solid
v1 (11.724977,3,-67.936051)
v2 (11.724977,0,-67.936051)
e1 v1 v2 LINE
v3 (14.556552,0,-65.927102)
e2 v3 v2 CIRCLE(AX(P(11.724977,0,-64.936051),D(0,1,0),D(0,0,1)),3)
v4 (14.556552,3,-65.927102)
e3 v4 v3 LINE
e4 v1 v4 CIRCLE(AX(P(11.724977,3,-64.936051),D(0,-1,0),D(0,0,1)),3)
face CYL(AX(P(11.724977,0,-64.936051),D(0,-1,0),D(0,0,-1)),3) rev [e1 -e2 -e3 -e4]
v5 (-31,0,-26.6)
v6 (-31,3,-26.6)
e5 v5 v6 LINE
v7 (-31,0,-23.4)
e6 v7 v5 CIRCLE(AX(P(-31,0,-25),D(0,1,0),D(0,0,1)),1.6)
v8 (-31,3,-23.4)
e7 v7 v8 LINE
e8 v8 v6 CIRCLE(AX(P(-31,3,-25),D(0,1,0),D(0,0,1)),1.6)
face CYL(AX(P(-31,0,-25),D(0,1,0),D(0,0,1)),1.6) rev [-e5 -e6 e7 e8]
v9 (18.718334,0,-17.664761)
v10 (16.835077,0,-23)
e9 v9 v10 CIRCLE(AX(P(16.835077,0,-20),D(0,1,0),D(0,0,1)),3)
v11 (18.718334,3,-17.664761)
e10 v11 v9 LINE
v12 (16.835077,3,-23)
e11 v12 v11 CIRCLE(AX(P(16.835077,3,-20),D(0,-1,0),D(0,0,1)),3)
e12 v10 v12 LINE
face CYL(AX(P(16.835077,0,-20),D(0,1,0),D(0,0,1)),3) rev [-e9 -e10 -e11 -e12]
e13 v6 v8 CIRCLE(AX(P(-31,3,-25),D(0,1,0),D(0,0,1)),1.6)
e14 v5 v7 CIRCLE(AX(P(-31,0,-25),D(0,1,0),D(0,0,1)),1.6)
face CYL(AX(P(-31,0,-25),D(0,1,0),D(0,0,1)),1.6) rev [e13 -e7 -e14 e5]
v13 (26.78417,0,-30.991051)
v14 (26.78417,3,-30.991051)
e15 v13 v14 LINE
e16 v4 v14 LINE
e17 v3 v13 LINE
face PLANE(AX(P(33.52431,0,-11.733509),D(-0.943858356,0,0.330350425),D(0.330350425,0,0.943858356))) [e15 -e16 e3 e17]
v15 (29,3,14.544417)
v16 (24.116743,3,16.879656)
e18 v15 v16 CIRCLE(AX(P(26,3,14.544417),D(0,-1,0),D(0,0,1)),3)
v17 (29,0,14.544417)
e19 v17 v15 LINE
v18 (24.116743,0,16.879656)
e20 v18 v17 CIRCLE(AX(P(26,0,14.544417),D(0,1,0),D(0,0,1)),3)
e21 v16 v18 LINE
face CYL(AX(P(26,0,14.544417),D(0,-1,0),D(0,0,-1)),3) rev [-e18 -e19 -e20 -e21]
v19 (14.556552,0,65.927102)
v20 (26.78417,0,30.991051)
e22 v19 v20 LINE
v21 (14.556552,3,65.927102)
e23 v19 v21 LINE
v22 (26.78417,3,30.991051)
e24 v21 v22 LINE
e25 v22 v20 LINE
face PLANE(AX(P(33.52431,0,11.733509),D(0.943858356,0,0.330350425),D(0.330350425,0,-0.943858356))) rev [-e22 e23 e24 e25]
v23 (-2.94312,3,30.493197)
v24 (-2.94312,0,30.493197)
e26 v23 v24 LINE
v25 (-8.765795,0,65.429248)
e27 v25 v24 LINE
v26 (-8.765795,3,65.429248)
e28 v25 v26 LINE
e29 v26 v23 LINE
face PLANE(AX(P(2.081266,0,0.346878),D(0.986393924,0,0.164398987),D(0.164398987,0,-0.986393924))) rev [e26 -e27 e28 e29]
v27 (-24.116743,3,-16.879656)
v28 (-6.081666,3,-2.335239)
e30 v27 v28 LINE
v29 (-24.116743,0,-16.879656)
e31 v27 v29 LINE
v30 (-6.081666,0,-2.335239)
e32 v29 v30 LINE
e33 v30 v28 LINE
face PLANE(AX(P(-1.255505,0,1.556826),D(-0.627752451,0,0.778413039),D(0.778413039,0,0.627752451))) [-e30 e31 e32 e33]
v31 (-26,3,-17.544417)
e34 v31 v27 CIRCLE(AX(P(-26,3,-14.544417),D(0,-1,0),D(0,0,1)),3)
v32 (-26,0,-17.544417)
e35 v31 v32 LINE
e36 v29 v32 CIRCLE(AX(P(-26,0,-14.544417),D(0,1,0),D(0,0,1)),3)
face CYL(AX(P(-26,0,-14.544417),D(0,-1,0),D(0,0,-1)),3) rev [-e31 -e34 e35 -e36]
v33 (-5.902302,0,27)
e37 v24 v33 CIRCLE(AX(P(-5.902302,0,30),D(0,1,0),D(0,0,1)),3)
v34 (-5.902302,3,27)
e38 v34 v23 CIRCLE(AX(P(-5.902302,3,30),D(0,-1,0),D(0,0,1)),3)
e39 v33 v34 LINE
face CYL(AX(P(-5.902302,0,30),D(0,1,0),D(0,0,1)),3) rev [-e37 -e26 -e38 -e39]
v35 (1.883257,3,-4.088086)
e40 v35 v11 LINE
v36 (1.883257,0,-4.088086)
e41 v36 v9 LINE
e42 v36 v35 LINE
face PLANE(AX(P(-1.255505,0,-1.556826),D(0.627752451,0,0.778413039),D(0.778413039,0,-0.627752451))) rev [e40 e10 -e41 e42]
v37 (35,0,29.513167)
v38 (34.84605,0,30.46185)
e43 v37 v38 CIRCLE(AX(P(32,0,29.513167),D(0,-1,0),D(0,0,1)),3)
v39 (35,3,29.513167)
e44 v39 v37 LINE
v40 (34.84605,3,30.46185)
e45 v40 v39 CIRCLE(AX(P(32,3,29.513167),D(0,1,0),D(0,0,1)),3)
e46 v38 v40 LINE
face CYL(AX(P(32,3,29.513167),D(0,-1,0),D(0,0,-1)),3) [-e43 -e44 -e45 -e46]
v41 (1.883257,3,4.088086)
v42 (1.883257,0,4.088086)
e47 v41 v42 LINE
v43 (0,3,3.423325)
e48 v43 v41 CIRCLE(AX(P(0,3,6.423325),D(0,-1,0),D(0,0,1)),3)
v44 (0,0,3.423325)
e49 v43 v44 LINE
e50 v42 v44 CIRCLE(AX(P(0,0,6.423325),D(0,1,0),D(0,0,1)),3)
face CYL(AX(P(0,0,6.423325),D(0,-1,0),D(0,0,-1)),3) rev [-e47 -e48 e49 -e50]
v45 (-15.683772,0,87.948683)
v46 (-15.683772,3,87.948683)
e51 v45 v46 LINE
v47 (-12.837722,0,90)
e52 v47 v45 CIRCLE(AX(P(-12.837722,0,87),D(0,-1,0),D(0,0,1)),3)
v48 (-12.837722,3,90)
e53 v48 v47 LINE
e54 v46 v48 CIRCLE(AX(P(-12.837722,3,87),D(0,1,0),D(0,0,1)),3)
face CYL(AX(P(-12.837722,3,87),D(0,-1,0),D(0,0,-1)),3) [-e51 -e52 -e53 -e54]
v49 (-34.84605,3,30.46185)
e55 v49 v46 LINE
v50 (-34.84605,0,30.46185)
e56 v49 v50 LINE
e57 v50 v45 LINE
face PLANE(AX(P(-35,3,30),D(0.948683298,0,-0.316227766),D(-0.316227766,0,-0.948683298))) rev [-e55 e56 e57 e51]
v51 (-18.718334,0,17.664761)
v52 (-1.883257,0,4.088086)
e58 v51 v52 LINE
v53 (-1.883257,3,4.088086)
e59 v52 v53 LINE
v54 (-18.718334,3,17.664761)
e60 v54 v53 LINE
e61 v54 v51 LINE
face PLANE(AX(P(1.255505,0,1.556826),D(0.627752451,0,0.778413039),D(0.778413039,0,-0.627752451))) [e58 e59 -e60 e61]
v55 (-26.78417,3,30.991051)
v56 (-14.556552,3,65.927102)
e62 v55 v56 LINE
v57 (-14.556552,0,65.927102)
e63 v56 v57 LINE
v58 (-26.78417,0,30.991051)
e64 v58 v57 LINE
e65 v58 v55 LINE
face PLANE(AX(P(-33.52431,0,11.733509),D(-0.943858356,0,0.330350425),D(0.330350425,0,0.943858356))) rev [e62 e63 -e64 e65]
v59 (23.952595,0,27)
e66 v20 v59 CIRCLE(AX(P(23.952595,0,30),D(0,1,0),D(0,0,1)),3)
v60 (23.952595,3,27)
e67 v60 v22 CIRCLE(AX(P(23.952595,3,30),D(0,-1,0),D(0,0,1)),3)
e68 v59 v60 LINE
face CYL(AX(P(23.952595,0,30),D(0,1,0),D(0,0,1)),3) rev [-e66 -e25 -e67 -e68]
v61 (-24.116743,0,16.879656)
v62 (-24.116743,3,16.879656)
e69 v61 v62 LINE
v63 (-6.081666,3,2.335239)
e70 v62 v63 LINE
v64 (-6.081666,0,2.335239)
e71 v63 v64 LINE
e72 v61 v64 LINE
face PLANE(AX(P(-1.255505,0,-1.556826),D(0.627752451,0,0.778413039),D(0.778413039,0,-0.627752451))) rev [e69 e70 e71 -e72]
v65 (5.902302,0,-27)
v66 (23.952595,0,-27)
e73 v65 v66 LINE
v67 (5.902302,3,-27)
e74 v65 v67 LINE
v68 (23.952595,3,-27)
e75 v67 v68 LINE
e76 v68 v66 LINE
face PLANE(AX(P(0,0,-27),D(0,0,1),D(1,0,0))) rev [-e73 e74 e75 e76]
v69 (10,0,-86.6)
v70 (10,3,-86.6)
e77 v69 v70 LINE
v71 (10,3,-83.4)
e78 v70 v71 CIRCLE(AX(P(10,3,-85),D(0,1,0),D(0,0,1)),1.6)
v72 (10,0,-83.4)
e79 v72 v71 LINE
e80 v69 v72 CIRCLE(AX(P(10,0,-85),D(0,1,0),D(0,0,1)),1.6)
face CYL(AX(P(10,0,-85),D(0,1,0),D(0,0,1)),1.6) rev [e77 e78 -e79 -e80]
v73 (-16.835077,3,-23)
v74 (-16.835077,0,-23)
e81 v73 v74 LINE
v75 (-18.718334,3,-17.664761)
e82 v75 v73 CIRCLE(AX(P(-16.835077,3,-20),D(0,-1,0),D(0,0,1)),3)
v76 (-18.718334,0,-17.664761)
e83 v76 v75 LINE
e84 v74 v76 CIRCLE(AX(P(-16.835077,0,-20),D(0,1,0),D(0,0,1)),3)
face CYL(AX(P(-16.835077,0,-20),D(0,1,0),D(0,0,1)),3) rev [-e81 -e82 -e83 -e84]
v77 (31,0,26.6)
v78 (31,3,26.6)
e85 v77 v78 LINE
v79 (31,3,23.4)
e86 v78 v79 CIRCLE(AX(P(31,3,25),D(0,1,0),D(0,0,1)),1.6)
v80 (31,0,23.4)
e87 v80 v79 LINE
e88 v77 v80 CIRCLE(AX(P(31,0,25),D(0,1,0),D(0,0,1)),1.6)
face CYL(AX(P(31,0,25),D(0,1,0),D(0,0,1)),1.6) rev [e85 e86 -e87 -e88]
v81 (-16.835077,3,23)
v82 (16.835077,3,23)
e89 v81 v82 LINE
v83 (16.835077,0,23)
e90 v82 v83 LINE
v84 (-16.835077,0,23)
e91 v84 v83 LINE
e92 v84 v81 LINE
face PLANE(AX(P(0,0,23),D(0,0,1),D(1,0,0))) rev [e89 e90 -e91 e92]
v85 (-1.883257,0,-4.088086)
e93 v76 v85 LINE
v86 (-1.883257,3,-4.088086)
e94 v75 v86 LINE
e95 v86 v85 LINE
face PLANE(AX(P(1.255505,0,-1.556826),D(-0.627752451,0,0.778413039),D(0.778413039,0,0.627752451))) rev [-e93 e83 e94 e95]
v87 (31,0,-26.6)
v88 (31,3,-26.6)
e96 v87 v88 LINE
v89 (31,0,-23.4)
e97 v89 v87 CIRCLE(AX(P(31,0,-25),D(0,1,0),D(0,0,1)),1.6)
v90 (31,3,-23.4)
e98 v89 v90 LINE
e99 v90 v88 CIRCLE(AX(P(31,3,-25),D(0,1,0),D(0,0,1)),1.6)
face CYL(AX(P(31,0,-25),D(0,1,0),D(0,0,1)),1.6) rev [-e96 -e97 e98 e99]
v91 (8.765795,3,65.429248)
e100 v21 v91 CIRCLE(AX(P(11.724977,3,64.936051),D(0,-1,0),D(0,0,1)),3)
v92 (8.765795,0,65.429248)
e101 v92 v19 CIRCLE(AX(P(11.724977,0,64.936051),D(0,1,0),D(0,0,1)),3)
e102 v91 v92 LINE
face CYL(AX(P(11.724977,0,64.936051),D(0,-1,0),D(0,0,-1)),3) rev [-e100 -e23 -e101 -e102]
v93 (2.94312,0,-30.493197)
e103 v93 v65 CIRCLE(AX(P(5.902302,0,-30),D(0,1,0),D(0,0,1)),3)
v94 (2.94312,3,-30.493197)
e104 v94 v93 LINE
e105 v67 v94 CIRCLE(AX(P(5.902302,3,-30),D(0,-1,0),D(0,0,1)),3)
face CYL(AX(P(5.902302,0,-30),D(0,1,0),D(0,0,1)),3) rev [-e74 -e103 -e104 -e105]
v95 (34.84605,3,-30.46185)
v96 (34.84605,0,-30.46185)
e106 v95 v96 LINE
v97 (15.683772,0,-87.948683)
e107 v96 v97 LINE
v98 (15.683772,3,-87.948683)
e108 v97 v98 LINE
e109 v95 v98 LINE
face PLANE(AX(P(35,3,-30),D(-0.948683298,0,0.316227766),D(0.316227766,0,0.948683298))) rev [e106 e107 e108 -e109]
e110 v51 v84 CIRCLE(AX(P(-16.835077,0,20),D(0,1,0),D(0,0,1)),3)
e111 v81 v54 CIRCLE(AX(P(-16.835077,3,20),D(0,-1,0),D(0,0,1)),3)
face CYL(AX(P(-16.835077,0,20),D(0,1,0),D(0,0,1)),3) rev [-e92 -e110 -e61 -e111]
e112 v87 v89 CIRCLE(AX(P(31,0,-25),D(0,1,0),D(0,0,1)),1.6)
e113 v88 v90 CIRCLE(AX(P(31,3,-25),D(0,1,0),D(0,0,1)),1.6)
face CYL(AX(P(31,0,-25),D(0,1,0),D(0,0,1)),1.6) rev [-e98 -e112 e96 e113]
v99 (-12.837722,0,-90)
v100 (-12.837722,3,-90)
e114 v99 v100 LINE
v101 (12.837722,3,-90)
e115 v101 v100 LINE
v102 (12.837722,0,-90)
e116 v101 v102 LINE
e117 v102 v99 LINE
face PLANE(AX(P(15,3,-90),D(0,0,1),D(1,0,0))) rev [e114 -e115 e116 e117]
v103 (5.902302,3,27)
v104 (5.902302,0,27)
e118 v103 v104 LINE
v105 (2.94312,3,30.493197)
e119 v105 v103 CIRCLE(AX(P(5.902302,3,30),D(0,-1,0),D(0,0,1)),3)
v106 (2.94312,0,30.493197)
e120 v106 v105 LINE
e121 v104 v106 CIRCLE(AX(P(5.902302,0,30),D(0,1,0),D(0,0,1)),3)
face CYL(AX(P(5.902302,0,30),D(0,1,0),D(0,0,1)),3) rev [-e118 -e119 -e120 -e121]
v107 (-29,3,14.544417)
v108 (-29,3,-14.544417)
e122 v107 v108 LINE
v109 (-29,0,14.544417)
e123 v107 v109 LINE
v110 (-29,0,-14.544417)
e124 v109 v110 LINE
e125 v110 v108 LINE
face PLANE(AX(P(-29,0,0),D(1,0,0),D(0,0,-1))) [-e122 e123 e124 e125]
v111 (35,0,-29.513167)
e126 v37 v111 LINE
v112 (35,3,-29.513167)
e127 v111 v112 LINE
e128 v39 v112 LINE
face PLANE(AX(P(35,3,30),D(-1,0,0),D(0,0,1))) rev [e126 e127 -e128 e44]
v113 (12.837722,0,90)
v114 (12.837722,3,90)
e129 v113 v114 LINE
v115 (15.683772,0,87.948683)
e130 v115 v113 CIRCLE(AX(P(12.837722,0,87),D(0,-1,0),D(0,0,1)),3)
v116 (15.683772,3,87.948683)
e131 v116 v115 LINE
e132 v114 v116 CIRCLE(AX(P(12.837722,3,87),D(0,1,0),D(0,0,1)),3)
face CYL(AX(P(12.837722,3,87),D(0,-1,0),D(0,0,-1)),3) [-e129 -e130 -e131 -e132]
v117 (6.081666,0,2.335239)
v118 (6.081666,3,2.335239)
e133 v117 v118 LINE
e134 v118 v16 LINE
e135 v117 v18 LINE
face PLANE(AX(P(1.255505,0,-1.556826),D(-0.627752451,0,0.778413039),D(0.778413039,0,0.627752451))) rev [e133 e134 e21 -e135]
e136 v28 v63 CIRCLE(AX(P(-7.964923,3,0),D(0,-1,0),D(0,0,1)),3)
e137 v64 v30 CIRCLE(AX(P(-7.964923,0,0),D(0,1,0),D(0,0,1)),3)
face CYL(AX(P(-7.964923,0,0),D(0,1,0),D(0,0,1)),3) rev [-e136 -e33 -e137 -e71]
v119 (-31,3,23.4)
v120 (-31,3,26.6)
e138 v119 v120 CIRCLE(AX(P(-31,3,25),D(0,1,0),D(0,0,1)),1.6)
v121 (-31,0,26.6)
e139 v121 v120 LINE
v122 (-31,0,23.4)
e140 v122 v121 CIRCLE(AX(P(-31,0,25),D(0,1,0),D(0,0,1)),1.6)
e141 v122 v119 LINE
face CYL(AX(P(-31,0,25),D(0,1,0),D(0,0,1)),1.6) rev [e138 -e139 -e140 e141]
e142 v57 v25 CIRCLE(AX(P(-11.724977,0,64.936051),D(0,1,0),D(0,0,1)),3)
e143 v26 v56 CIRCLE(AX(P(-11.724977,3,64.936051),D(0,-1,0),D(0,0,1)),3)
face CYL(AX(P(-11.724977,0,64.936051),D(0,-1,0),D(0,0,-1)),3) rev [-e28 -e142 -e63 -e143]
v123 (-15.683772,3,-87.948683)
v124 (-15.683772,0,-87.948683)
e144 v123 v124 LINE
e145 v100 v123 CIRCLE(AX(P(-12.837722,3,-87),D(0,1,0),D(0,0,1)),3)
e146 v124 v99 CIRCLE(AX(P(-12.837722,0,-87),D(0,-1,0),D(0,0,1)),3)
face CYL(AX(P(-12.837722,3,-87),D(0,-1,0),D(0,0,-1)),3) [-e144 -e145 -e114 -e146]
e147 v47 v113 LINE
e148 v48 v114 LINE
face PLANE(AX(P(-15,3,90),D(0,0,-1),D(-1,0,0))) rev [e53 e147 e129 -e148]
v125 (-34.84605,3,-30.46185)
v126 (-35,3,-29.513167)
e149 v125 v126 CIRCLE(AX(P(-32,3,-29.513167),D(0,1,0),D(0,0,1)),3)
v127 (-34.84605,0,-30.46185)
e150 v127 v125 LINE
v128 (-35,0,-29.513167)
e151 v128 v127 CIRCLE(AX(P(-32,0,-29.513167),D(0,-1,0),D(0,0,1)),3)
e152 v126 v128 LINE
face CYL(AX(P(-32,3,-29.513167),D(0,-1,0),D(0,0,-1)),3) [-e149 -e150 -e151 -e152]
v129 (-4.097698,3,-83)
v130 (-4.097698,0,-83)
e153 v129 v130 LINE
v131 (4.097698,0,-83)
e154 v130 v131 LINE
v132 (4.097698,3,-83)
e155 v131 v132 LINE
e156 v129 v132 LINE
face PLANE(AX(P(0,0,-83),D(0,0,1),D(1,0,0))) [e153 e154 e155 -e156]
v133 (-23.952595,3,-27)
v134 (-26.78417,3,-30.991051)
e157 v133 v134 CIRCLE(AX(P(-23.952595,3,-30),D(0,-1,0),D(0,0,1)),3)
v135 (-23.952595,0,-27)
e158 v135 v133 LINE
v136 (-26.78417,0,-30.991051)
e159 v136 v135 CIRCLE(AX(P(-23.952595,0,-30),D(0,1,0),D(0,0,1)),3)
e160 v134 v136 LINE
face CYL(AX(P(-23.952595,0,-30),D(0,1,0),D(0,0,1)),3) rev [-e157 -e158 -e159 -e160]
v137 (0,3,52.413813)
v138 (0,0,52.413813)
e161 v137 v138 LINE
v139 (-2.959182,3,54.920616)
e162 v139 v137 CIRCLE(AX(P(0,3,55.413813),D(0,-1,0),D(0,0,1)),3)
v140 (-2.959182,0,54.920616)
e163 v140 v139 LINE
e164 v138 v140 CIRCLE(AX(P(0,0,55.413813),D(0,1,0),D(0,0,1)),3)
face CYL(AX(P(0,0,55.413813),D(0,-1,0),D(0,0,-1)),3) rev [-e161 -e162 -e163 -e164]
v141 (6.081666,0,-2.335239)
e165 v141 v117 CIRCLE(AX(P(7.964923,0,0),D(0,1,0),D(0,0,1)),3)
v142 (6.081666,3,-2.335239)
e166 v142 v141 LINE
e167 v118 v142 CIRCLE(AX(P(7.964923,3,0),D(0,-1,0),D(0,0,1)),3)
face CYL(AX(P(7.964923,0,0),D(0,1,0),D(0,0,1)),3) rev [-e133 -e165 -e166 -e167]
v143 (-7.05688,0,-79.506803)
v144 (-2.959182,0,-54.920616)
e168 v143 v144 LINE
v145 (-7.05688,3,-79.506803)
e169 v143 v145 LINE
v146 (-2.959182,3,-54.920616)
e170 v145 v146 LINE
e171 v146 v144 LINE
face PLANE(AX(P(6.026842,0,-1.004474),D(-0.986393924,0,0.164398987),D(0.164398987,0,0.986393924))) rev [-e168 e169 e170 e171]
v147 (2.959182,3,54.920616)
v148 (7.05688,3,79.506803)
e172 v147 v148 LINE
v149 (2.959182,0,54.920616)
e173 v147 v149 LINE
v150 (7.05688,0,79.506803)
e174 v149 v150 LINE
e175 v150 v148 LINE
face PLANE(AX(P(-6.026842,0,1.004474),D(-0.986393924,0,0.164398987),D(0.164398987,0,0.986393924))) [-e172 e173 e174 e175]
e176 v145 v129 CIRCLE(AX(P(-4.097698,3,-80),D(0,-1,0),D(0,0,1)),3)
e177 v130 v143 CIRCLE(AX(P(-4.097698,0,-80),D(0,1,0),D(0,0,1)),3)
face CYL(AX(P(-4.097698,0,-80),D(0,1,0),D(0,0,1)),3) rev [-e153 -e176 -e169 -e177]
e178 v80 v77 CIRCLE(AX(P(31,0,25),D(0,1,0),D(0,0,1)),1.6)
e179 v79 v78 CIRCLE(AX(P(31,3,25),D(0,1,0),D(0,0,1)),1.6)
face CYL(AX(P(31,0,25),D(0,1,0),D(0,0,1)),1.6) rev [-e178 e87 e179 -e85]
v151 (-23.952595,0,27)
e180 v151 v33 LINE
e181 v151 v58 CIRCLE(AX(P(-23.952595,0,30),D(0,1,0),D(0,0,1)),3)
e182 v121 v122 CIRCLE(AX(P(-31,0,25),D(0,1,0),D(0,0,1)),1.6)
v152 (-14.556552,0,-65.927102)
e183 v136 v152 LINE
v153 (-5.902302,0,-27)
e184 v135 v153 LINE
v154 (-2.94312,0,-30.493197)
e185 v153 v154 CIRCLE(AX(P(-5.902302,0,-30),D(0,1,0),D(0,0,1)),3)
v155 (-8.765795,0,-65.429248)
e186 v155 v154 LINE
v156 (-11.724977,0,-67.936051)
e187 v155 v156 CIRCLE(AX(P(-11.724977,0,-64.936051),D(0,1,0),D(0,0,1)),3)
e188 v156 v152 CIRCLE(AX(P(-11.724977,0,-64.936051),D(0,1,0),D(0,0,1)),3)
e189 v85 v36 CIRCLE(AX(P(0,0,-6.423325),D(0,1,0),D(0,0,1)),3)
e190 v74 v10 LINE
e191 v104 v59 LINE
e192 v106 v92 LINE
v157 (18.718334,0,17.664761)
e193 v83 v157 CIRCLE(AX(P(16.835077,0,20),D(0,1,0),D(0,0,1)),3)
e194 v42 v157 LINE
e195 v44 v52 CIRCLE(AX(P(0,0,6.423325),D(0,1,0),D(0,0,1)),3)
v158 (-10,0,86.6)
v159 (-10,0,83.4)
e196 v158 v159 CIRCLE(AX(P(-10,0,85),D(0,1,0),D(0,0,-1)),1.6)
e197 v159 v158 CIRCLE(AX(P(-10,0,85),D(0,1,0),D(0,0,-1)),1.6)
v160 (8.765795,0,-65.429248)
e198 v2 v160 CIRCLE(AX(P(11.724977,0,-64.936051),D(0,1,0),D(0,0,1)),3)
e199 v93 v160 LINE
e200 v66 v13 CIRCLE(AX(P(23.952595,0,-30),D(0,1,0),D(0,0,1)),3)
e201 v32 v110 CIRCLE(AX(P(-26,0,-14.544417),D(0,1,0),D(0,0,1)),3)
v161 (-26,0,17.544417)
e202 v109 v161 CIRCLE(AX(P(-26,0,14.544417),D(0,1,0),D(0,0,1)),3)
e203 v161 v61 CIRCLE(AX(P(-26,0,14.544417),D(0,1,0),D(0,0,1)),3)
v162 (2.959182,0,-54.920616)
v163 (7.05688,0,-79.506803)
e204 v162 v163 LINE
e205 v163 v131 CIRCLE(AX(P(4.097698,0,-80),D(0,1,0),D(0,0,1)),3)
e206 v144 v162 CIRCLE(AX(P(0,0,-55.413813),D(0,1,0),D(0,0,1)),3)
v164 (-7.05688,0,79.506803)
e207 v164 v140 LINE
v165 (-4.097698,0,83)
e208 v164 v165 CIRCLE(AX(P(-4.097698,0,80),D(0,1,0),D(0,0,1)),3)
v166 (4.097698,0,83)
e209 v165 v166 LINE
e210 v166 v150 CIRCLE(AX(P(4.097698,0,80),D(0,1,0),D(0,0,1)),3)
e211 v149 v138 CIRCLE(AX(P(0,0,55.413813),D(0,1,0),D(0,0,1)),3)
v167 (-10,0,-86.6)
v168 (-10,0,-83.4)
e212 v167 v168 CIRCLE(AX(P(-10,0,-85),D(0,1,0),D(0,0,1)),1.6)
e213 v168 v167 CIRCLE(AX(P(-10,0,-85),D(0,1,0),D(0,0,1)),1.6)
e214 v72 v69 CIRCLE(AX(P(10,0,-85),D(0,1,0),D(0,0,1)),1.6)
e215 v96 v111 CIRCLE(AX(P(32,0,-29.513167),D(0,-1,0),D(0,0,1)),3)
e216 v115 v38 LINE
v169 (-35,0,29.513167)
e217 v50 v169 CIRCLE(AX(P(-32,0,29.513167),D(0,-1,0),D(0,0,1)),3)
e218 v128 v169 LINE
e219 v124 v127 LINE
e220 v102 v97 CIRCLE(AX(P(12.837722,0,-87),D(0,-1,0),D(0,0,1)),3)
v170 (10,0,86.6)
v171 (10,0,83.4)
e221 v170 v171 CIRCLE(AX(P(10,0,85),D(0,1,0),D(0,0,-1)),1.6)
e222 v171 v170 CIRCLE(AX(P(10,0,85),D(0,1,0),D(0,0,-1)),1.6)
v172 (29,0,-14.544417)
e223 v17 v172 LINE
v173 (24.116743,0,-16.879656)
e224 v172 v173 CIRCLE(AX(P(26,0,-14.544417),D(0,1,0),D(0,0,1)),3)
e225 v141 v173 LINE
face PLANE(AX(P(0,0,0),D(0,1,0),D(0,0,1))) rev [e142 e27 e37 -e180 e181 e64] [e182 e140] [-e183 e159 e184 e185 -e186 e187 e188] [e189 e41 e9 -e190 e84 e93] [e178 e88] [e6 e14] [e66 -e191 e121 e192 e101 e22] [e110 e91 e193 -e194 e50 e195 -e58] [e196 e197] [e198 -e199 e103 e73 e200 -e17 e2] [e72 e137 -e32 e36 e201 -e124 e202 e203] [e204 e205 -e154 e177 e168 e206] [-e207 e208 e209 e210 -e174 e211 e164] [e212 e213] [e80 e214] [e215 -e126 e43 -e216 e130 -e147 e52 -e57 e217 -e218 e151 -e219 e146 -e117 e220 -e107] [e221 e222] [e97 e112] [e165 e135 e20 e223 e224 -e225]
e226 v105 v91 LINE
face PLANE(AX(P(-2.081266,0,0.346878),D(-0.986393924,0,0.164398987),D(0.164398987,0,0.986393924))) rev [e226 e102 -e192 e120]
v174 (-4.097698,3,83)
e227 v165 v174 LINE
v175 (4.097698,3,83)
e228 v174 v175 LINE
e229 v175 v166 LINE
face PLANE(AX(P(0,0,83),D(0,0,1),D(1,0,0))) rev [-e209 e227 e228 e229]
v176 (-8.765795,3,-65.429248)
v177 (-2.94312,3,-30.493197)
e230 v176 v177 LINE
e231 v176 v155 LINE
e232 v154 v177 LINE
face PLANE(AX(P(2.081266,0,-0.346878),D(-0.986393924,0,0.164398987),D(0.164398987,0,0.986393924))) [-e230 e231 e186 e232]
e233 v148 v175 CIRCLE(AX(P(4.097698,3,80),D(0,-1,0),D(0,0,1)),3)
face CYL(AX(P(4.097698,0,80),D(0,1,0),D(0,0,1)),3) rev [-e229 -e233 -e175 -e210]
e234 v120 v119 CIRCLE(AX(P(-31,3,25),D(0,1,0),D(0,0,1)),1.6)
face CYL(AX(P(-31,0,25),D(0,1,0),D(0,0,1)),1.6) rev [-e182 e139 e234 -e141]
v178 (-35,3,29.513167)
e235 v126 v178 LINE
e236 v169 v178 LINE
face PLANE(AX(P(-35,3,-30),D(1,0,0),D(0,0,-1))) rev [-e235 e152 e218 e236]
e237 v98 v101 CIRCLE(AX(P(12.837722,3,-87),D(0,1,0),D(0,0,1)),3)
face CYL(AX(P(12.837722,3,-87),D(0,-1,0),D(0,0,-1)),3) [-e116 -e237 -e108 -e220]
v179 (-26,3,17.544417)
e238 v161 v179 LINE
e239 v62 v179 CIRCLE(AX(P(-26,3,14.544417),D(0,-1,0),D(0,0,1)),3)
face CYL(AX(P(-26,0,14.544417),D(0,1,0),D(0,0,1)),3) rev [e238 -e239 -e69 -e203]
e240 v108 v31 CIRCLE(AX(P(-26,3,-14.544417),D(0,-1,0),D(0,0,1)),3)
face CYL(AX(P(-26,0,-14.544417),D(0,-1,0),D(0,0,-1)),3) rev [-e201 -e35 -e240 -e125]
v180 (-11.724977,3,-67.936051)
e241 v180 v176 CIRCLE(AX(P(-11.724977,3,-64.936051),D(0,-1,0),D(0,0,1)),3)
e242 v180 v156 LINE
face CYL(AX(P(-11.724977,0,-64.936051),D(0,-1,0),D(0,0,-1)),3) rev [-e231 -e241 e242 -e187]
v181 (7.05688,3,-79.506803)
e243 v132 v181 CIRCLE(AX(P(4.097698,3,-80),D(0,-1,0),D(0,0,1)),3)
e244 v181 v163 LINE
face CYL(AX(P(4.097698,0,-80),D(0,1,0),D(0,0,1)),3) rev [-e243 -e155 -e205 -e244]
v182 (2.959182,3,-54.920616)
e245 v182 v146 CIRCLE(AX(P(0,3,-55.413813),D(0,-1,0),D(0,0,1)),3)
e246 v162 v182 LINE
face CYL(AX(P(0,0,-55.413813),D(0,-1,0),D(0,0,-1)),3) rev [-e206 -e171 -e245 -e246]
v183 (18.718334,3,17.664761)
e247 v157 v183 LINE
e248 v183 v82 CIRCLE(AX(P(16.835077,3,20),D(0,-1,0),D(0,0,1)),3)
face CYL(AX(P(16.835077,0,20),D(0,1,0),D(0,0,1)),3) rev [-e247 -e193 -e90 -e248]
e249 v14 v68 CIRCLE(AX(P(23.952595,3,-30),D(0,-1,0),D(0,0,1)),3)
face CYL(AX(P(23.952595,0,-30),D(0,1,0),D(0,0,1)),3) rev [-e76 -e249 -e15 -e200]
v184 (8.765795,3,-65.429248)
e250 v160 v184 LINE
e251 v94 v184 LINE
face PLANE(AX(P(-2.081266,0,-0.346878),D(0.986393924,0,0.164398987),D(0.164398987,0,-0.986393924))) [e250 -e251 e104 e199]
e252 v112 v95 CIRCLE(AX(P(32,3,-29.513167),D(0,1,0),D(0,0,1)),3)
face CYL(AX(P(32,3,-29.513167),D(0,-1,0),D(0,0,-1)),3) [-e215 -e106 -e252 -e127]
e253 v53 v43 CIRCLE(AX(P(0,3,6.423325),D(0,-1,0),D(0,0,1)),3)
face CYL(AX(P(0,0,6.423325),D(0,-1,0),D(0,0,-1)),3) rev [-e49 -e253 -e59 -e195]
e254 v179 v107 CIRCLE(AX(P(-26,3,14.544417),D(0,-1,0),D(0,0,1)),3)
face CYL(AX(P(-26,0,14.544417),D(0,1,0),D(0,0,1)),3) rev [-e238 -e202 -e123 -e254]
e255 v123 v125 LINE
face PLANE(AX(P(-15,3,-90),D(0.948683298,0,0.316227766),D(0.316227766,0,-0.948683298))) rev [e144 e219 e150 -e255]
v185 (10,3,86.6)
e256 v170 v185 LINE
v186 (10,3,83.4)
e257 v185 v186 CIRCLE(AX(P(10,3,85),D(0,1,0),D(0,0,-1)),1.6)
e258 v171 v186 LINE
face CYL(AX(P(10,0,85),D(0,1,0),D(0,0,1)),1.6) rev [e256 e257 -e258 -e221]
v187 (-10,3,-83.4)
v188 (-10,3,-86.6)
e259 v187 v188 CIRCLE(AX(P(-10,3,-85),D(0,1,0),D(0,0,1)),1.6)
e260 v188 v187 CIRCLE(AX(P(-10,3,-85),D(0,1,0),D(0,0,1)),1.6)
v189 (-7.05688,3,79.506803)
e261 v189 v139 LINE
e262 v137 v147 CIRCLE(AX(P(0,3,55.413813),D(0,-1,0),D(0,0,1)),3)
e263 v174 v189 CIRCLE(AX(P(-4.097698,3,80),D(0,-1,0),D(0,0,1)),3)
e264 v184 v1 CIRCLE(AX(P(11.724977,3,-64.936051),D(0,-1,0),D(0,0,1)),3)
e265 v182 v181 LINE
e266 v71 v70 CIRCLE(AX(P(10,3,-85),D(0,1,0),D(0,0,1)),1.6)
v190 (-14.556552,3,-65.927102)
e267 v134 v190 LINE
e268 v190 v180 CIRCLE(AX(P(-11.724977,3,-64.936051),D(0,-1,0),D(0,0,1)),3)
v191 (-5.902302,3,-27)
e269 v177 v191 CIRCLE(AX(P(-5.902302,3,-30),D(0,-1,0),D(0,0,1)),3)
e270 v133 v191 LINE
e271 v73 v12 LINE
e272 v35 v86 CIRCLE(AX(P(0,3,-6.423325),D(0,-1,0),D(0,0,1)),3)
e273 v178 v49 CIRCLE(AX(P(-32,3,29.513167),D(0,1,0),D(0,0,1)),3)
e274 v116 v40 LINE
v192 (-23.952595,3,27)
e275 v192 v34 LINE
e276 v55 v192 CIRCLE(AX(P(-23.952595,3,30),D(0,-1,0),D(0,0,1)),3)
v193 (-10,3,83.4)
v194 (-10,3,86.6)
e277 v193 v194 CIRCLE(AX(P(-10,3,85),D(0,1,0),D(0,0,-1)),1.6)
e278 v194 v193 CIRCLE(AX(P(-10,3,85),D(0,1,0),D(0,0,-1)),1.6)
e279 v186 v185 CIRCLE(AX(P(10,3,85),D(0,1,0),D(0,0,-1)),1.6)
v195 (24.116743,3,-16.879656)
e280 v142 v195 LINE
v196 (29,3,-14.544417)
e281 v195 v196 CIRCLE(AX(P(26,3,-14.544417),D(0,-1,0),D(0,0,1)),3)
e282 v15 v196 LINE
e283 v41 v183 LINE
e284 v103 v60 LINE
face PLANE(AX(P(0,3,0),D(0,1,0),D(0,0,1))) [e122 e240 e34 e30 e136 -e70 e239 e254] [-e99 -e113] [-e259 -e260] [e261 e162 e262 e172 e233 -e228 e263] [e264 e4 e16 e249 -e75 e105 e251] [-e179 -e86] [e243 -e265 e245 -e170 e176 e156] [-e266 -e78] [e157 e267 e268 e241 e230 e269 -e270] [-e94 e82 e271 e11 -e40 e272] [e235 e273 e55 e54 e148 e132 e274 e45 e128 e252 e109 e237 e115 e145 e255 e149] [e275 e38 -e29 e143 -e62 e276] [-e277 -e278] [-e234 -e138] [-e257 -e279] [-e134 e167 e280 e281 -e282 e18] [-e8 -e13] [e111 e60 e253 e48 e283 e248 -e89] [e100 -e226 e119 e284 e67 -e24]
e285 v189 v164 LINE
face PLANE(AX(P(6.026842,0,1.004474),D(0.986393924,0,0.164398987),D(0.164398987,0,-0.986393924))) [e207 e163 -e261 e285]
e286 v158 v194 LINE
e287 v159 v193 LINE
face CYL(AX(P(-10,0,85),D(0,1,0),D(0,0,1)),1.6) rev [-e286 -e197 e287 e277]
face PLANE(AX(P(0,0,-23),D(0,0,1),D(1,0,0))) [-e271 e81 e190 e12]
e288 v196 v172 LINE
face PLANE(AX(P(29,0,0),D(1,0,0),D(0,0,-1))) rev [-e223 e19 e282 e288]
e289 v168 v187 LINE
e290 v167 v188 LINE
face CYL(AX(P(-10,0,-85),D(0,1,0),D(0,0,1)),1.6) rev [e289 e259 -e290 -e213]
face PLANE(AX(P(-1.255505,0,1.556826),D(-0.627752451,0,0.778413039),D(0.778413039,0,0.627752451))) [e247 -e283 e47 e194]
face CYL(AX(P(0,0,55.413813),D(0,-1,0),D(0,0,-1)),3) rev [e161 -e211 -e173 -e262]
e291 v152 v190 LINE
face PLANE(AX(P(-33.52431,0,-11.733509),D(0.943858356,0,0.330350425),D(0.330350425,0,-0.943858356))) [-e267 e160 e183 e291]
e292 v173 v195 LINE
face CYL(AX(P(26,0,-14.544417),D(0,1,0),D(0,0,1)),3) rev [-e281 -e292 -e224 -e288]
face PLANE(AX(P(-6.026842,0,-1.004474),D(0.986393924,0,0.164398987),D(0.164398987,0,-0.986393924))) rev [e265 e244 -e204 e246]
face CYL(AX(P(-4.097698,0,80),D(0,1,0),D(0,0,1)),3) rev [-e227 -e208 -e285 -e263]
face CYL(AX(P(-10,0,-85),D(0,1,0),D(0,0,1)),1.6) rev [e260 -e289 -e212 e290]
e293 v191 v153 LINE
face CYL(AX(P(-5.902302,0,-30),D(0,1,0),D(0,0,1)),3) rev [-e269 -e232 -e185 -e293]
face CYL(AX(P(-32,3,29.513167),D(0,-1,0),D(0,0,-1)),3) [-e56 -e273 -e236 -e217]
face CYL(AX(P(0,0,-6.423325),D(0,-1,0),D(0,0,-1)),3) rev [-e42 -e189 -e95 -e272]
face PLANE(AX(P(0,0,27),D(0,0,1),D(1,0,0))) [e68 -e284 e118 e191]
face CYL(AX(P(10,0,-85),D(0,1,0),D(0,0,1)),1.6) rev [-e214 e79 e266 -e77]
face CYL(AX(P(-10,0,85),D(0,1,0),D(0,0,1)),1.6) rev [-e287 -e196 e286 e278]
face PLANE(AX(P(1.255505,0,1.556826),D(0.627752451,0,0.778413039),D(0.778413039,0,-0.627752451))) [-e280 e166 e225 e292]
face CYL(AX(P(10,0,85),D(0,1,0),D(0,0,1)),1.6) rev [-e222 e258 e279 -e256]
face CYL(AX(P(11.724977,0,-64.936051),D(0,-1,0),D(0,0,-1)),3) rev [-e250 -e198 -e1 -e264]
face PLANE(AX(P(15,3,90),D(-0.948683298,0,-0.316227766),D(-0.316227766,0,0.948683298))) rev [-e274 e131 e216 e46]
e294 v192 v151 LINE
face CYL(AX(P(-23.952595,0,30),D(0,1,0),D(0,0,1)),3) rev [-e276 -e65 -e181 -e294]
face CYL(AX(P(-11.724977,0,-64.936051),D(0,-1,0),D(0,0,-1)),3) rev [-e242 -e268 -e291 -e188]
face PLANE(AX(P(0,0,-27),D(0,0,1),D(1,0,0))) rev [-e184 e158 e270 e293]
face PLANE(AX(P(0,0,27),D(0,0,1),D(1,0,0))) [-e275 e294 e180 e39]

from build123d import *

# Parameters (mm, degrees)
EXTRUDE_1_DEPTH     = 3
SKETCH_2_R          = 1.6
CUT_EXTRUDE_1_DEPTH = 3
CUT_EXTRUDE_2_DEPTH = 3
FILLET_1_R          = 3


with BuildPart() as part:
    # 草图1 → 凸台-拉伸1 (new body)
    with BuildSketch(Plane(origin=(0, 0, 0), x_dir=(1, 0, 0), z_dir=(0, 1, 0))):
        Polygon((-15, 90), (-35, 30), (-35, -30), (-15, -90), (15, -90), (35, -30), (35, 30), (15, 90), align=None)
    extrude(amount=EXTRUDE_1_DEPTH)

    # 草图2 → 切除-拉伸1 (cut)
    with BuildSketch(Plane(origin=(0, 3, 0), x_dir=(1, 0, 0), z_dir=(0, 1, 0))):
        with Locations(Location((-31, 25, 0), (0, 0, 270))):
            Circle(SKETCH_2_R)
        with Locations(Location((31, 25, 0), (0, 0, 270))):
            Circle(SKETCH_2_R)
        with Locations(Location((31, -25, 0), (0, 0, 270))):
            Circle(SKETCH_2_R)
        with Locations(Location((-31, -25, 0), (0, 0, 270))):
            Circle(SKETCH_2_R)
        with Locations(Location((-10, 85, 0), (0, 0, 270))):
            Circle(SKETCH_2_R)
        with Locations(Location((10, 85, 0), (0, 0, 270))):
            Circle(SKETCH_2_R)
        with Locations(Location((10, -85, 0), (0, 0, 90))):
            Circle(SKETCH_2_R)
        with Locations(Location((-10, -85, 0), (0, 0, 90))):
            Circle(SKETCH_2_R)
    extrude(amount=-CUT_EXTRUDE_1_DEPTH, mode=Mode.SUBTRACT)

    # 草图4 → 切除-拉伸2 (cut)
    with BuildSketch(Plane(origin=(0, 3, 0), x_dir=(1, 0, 0), z_dir=(0, 1, 0))):
        Polygon((-10.689990891, 76.974420284), (-28.18103799, 27), (-2.360920843, 27), align=None)
        Polygon((10.689990891, 76.974420284), (2.360920843, 27), (28.18103799, 27), align=None)
        Polygon((7.639079157, 83), (-7.639079157, 83), (0, 37.165525061), align=None)
        Polygon((-1.694254177, 23), (-25.33403076, 23), (0, 2.569330032), (25.33403076, 23), (1.694254177, 23), (0, 12.834474939), align=None)
        Polygon((1.694254177, 23), (-1.694254177, 23), (0, 12.834474939), align=None)
        Polygon((-3.18596924, 0), (-29, 20.817766742), (-29, -20.817766742), align=None)
        Polygon((29, 20.817766742), (3.18596924, 0), (29, -20.817766742), align=None)
        Polygon((25.33403076, -23), (0, -2.569330032), (-25.33403076, -23), (-1.694254177, -23), (0, -12.834474939), (1.694254177, -23), align=None)
        Polygon((0, -12.834474939), (-1.694254177, -23), (1.694254177, -23), align=None)
        Polygon((-2.360920843, -27), (-28.18103799, -27), (-10.689990891, -76.974420284), align=None)
        Polygon((10.689990891, -76.974420284), (28.18103799, -27), (2.360920843, -27), align=None)
        Polygon((0, -37.165525061), (-7.639079157, -83), (7.639079157, -83), align=None)
    extrude(amount=-CUT_EXTRUDE_2_DEPTH, mode=Mode.SUBTRACT)

    # 圆角1
    fillet_1_edges = [part.edges().sort_by_distance(p)[0] for p in [
        (-28.18103799, 1.5, 27),
        (-2.360920843, 1.5, 27),
        (-10.689990891, 1.5, 76.974420284),
        (3.18596924, 1.5, 0),
        (29, 1.5, -20.817766742),
        (29, 1.5, 20.817766742),
        (-25.33403076, 1.5, 23),
        (0, 1.5, 2.569330032),
        (25.33403076, 1.5, 23),
        (25.33403076, 1.5, -23),
        (0, 1.5, -2.569330032),
        (-25.33403076, 1.5, -23),
        (-29, 1.5, 20.817766742),
        (-29, 1.5, -20.817766742),
        (-3.18596924, 1.5, 0),
        (2.360920843, 1.5, -27),
        (10.689990891, 1.5, -76.974420284),
        (28.18103799, 1.5, -27),
        (-7.639079157, 1.5, -83),
        (7.639079157, 1.5, -83),
        (0, 1.5, -37.165525061),
        (-7.639079157, 1.5, 83),
        (0, 1.5, 37.165525061),
        (7.639079157, 1.5, 83),
        (-28.18103799, 1.5, -27),
        (-10.689990891, 1.5, -76.974420284),
        (-2.360920843, 1.5, -27),
        (15, 1.5, -90),
        (35, 1.5, -30),
        (35, 1.5, 30),
        (15, 1.5, 90),
        (-15, 1.5, 90),
        (-35, 1.5, 30),
        (-35, 1.5, -30),
        (-15, 1.5, -90),
        (10.689990891, 1.5, 76.974420284),
        (2.360920843, 1.5, 27),
        (28.18103799, 1.5, 27),
    ]]
    fillet(fillet_1_edges, radius=FILLET_1_R)


solid = part.part
